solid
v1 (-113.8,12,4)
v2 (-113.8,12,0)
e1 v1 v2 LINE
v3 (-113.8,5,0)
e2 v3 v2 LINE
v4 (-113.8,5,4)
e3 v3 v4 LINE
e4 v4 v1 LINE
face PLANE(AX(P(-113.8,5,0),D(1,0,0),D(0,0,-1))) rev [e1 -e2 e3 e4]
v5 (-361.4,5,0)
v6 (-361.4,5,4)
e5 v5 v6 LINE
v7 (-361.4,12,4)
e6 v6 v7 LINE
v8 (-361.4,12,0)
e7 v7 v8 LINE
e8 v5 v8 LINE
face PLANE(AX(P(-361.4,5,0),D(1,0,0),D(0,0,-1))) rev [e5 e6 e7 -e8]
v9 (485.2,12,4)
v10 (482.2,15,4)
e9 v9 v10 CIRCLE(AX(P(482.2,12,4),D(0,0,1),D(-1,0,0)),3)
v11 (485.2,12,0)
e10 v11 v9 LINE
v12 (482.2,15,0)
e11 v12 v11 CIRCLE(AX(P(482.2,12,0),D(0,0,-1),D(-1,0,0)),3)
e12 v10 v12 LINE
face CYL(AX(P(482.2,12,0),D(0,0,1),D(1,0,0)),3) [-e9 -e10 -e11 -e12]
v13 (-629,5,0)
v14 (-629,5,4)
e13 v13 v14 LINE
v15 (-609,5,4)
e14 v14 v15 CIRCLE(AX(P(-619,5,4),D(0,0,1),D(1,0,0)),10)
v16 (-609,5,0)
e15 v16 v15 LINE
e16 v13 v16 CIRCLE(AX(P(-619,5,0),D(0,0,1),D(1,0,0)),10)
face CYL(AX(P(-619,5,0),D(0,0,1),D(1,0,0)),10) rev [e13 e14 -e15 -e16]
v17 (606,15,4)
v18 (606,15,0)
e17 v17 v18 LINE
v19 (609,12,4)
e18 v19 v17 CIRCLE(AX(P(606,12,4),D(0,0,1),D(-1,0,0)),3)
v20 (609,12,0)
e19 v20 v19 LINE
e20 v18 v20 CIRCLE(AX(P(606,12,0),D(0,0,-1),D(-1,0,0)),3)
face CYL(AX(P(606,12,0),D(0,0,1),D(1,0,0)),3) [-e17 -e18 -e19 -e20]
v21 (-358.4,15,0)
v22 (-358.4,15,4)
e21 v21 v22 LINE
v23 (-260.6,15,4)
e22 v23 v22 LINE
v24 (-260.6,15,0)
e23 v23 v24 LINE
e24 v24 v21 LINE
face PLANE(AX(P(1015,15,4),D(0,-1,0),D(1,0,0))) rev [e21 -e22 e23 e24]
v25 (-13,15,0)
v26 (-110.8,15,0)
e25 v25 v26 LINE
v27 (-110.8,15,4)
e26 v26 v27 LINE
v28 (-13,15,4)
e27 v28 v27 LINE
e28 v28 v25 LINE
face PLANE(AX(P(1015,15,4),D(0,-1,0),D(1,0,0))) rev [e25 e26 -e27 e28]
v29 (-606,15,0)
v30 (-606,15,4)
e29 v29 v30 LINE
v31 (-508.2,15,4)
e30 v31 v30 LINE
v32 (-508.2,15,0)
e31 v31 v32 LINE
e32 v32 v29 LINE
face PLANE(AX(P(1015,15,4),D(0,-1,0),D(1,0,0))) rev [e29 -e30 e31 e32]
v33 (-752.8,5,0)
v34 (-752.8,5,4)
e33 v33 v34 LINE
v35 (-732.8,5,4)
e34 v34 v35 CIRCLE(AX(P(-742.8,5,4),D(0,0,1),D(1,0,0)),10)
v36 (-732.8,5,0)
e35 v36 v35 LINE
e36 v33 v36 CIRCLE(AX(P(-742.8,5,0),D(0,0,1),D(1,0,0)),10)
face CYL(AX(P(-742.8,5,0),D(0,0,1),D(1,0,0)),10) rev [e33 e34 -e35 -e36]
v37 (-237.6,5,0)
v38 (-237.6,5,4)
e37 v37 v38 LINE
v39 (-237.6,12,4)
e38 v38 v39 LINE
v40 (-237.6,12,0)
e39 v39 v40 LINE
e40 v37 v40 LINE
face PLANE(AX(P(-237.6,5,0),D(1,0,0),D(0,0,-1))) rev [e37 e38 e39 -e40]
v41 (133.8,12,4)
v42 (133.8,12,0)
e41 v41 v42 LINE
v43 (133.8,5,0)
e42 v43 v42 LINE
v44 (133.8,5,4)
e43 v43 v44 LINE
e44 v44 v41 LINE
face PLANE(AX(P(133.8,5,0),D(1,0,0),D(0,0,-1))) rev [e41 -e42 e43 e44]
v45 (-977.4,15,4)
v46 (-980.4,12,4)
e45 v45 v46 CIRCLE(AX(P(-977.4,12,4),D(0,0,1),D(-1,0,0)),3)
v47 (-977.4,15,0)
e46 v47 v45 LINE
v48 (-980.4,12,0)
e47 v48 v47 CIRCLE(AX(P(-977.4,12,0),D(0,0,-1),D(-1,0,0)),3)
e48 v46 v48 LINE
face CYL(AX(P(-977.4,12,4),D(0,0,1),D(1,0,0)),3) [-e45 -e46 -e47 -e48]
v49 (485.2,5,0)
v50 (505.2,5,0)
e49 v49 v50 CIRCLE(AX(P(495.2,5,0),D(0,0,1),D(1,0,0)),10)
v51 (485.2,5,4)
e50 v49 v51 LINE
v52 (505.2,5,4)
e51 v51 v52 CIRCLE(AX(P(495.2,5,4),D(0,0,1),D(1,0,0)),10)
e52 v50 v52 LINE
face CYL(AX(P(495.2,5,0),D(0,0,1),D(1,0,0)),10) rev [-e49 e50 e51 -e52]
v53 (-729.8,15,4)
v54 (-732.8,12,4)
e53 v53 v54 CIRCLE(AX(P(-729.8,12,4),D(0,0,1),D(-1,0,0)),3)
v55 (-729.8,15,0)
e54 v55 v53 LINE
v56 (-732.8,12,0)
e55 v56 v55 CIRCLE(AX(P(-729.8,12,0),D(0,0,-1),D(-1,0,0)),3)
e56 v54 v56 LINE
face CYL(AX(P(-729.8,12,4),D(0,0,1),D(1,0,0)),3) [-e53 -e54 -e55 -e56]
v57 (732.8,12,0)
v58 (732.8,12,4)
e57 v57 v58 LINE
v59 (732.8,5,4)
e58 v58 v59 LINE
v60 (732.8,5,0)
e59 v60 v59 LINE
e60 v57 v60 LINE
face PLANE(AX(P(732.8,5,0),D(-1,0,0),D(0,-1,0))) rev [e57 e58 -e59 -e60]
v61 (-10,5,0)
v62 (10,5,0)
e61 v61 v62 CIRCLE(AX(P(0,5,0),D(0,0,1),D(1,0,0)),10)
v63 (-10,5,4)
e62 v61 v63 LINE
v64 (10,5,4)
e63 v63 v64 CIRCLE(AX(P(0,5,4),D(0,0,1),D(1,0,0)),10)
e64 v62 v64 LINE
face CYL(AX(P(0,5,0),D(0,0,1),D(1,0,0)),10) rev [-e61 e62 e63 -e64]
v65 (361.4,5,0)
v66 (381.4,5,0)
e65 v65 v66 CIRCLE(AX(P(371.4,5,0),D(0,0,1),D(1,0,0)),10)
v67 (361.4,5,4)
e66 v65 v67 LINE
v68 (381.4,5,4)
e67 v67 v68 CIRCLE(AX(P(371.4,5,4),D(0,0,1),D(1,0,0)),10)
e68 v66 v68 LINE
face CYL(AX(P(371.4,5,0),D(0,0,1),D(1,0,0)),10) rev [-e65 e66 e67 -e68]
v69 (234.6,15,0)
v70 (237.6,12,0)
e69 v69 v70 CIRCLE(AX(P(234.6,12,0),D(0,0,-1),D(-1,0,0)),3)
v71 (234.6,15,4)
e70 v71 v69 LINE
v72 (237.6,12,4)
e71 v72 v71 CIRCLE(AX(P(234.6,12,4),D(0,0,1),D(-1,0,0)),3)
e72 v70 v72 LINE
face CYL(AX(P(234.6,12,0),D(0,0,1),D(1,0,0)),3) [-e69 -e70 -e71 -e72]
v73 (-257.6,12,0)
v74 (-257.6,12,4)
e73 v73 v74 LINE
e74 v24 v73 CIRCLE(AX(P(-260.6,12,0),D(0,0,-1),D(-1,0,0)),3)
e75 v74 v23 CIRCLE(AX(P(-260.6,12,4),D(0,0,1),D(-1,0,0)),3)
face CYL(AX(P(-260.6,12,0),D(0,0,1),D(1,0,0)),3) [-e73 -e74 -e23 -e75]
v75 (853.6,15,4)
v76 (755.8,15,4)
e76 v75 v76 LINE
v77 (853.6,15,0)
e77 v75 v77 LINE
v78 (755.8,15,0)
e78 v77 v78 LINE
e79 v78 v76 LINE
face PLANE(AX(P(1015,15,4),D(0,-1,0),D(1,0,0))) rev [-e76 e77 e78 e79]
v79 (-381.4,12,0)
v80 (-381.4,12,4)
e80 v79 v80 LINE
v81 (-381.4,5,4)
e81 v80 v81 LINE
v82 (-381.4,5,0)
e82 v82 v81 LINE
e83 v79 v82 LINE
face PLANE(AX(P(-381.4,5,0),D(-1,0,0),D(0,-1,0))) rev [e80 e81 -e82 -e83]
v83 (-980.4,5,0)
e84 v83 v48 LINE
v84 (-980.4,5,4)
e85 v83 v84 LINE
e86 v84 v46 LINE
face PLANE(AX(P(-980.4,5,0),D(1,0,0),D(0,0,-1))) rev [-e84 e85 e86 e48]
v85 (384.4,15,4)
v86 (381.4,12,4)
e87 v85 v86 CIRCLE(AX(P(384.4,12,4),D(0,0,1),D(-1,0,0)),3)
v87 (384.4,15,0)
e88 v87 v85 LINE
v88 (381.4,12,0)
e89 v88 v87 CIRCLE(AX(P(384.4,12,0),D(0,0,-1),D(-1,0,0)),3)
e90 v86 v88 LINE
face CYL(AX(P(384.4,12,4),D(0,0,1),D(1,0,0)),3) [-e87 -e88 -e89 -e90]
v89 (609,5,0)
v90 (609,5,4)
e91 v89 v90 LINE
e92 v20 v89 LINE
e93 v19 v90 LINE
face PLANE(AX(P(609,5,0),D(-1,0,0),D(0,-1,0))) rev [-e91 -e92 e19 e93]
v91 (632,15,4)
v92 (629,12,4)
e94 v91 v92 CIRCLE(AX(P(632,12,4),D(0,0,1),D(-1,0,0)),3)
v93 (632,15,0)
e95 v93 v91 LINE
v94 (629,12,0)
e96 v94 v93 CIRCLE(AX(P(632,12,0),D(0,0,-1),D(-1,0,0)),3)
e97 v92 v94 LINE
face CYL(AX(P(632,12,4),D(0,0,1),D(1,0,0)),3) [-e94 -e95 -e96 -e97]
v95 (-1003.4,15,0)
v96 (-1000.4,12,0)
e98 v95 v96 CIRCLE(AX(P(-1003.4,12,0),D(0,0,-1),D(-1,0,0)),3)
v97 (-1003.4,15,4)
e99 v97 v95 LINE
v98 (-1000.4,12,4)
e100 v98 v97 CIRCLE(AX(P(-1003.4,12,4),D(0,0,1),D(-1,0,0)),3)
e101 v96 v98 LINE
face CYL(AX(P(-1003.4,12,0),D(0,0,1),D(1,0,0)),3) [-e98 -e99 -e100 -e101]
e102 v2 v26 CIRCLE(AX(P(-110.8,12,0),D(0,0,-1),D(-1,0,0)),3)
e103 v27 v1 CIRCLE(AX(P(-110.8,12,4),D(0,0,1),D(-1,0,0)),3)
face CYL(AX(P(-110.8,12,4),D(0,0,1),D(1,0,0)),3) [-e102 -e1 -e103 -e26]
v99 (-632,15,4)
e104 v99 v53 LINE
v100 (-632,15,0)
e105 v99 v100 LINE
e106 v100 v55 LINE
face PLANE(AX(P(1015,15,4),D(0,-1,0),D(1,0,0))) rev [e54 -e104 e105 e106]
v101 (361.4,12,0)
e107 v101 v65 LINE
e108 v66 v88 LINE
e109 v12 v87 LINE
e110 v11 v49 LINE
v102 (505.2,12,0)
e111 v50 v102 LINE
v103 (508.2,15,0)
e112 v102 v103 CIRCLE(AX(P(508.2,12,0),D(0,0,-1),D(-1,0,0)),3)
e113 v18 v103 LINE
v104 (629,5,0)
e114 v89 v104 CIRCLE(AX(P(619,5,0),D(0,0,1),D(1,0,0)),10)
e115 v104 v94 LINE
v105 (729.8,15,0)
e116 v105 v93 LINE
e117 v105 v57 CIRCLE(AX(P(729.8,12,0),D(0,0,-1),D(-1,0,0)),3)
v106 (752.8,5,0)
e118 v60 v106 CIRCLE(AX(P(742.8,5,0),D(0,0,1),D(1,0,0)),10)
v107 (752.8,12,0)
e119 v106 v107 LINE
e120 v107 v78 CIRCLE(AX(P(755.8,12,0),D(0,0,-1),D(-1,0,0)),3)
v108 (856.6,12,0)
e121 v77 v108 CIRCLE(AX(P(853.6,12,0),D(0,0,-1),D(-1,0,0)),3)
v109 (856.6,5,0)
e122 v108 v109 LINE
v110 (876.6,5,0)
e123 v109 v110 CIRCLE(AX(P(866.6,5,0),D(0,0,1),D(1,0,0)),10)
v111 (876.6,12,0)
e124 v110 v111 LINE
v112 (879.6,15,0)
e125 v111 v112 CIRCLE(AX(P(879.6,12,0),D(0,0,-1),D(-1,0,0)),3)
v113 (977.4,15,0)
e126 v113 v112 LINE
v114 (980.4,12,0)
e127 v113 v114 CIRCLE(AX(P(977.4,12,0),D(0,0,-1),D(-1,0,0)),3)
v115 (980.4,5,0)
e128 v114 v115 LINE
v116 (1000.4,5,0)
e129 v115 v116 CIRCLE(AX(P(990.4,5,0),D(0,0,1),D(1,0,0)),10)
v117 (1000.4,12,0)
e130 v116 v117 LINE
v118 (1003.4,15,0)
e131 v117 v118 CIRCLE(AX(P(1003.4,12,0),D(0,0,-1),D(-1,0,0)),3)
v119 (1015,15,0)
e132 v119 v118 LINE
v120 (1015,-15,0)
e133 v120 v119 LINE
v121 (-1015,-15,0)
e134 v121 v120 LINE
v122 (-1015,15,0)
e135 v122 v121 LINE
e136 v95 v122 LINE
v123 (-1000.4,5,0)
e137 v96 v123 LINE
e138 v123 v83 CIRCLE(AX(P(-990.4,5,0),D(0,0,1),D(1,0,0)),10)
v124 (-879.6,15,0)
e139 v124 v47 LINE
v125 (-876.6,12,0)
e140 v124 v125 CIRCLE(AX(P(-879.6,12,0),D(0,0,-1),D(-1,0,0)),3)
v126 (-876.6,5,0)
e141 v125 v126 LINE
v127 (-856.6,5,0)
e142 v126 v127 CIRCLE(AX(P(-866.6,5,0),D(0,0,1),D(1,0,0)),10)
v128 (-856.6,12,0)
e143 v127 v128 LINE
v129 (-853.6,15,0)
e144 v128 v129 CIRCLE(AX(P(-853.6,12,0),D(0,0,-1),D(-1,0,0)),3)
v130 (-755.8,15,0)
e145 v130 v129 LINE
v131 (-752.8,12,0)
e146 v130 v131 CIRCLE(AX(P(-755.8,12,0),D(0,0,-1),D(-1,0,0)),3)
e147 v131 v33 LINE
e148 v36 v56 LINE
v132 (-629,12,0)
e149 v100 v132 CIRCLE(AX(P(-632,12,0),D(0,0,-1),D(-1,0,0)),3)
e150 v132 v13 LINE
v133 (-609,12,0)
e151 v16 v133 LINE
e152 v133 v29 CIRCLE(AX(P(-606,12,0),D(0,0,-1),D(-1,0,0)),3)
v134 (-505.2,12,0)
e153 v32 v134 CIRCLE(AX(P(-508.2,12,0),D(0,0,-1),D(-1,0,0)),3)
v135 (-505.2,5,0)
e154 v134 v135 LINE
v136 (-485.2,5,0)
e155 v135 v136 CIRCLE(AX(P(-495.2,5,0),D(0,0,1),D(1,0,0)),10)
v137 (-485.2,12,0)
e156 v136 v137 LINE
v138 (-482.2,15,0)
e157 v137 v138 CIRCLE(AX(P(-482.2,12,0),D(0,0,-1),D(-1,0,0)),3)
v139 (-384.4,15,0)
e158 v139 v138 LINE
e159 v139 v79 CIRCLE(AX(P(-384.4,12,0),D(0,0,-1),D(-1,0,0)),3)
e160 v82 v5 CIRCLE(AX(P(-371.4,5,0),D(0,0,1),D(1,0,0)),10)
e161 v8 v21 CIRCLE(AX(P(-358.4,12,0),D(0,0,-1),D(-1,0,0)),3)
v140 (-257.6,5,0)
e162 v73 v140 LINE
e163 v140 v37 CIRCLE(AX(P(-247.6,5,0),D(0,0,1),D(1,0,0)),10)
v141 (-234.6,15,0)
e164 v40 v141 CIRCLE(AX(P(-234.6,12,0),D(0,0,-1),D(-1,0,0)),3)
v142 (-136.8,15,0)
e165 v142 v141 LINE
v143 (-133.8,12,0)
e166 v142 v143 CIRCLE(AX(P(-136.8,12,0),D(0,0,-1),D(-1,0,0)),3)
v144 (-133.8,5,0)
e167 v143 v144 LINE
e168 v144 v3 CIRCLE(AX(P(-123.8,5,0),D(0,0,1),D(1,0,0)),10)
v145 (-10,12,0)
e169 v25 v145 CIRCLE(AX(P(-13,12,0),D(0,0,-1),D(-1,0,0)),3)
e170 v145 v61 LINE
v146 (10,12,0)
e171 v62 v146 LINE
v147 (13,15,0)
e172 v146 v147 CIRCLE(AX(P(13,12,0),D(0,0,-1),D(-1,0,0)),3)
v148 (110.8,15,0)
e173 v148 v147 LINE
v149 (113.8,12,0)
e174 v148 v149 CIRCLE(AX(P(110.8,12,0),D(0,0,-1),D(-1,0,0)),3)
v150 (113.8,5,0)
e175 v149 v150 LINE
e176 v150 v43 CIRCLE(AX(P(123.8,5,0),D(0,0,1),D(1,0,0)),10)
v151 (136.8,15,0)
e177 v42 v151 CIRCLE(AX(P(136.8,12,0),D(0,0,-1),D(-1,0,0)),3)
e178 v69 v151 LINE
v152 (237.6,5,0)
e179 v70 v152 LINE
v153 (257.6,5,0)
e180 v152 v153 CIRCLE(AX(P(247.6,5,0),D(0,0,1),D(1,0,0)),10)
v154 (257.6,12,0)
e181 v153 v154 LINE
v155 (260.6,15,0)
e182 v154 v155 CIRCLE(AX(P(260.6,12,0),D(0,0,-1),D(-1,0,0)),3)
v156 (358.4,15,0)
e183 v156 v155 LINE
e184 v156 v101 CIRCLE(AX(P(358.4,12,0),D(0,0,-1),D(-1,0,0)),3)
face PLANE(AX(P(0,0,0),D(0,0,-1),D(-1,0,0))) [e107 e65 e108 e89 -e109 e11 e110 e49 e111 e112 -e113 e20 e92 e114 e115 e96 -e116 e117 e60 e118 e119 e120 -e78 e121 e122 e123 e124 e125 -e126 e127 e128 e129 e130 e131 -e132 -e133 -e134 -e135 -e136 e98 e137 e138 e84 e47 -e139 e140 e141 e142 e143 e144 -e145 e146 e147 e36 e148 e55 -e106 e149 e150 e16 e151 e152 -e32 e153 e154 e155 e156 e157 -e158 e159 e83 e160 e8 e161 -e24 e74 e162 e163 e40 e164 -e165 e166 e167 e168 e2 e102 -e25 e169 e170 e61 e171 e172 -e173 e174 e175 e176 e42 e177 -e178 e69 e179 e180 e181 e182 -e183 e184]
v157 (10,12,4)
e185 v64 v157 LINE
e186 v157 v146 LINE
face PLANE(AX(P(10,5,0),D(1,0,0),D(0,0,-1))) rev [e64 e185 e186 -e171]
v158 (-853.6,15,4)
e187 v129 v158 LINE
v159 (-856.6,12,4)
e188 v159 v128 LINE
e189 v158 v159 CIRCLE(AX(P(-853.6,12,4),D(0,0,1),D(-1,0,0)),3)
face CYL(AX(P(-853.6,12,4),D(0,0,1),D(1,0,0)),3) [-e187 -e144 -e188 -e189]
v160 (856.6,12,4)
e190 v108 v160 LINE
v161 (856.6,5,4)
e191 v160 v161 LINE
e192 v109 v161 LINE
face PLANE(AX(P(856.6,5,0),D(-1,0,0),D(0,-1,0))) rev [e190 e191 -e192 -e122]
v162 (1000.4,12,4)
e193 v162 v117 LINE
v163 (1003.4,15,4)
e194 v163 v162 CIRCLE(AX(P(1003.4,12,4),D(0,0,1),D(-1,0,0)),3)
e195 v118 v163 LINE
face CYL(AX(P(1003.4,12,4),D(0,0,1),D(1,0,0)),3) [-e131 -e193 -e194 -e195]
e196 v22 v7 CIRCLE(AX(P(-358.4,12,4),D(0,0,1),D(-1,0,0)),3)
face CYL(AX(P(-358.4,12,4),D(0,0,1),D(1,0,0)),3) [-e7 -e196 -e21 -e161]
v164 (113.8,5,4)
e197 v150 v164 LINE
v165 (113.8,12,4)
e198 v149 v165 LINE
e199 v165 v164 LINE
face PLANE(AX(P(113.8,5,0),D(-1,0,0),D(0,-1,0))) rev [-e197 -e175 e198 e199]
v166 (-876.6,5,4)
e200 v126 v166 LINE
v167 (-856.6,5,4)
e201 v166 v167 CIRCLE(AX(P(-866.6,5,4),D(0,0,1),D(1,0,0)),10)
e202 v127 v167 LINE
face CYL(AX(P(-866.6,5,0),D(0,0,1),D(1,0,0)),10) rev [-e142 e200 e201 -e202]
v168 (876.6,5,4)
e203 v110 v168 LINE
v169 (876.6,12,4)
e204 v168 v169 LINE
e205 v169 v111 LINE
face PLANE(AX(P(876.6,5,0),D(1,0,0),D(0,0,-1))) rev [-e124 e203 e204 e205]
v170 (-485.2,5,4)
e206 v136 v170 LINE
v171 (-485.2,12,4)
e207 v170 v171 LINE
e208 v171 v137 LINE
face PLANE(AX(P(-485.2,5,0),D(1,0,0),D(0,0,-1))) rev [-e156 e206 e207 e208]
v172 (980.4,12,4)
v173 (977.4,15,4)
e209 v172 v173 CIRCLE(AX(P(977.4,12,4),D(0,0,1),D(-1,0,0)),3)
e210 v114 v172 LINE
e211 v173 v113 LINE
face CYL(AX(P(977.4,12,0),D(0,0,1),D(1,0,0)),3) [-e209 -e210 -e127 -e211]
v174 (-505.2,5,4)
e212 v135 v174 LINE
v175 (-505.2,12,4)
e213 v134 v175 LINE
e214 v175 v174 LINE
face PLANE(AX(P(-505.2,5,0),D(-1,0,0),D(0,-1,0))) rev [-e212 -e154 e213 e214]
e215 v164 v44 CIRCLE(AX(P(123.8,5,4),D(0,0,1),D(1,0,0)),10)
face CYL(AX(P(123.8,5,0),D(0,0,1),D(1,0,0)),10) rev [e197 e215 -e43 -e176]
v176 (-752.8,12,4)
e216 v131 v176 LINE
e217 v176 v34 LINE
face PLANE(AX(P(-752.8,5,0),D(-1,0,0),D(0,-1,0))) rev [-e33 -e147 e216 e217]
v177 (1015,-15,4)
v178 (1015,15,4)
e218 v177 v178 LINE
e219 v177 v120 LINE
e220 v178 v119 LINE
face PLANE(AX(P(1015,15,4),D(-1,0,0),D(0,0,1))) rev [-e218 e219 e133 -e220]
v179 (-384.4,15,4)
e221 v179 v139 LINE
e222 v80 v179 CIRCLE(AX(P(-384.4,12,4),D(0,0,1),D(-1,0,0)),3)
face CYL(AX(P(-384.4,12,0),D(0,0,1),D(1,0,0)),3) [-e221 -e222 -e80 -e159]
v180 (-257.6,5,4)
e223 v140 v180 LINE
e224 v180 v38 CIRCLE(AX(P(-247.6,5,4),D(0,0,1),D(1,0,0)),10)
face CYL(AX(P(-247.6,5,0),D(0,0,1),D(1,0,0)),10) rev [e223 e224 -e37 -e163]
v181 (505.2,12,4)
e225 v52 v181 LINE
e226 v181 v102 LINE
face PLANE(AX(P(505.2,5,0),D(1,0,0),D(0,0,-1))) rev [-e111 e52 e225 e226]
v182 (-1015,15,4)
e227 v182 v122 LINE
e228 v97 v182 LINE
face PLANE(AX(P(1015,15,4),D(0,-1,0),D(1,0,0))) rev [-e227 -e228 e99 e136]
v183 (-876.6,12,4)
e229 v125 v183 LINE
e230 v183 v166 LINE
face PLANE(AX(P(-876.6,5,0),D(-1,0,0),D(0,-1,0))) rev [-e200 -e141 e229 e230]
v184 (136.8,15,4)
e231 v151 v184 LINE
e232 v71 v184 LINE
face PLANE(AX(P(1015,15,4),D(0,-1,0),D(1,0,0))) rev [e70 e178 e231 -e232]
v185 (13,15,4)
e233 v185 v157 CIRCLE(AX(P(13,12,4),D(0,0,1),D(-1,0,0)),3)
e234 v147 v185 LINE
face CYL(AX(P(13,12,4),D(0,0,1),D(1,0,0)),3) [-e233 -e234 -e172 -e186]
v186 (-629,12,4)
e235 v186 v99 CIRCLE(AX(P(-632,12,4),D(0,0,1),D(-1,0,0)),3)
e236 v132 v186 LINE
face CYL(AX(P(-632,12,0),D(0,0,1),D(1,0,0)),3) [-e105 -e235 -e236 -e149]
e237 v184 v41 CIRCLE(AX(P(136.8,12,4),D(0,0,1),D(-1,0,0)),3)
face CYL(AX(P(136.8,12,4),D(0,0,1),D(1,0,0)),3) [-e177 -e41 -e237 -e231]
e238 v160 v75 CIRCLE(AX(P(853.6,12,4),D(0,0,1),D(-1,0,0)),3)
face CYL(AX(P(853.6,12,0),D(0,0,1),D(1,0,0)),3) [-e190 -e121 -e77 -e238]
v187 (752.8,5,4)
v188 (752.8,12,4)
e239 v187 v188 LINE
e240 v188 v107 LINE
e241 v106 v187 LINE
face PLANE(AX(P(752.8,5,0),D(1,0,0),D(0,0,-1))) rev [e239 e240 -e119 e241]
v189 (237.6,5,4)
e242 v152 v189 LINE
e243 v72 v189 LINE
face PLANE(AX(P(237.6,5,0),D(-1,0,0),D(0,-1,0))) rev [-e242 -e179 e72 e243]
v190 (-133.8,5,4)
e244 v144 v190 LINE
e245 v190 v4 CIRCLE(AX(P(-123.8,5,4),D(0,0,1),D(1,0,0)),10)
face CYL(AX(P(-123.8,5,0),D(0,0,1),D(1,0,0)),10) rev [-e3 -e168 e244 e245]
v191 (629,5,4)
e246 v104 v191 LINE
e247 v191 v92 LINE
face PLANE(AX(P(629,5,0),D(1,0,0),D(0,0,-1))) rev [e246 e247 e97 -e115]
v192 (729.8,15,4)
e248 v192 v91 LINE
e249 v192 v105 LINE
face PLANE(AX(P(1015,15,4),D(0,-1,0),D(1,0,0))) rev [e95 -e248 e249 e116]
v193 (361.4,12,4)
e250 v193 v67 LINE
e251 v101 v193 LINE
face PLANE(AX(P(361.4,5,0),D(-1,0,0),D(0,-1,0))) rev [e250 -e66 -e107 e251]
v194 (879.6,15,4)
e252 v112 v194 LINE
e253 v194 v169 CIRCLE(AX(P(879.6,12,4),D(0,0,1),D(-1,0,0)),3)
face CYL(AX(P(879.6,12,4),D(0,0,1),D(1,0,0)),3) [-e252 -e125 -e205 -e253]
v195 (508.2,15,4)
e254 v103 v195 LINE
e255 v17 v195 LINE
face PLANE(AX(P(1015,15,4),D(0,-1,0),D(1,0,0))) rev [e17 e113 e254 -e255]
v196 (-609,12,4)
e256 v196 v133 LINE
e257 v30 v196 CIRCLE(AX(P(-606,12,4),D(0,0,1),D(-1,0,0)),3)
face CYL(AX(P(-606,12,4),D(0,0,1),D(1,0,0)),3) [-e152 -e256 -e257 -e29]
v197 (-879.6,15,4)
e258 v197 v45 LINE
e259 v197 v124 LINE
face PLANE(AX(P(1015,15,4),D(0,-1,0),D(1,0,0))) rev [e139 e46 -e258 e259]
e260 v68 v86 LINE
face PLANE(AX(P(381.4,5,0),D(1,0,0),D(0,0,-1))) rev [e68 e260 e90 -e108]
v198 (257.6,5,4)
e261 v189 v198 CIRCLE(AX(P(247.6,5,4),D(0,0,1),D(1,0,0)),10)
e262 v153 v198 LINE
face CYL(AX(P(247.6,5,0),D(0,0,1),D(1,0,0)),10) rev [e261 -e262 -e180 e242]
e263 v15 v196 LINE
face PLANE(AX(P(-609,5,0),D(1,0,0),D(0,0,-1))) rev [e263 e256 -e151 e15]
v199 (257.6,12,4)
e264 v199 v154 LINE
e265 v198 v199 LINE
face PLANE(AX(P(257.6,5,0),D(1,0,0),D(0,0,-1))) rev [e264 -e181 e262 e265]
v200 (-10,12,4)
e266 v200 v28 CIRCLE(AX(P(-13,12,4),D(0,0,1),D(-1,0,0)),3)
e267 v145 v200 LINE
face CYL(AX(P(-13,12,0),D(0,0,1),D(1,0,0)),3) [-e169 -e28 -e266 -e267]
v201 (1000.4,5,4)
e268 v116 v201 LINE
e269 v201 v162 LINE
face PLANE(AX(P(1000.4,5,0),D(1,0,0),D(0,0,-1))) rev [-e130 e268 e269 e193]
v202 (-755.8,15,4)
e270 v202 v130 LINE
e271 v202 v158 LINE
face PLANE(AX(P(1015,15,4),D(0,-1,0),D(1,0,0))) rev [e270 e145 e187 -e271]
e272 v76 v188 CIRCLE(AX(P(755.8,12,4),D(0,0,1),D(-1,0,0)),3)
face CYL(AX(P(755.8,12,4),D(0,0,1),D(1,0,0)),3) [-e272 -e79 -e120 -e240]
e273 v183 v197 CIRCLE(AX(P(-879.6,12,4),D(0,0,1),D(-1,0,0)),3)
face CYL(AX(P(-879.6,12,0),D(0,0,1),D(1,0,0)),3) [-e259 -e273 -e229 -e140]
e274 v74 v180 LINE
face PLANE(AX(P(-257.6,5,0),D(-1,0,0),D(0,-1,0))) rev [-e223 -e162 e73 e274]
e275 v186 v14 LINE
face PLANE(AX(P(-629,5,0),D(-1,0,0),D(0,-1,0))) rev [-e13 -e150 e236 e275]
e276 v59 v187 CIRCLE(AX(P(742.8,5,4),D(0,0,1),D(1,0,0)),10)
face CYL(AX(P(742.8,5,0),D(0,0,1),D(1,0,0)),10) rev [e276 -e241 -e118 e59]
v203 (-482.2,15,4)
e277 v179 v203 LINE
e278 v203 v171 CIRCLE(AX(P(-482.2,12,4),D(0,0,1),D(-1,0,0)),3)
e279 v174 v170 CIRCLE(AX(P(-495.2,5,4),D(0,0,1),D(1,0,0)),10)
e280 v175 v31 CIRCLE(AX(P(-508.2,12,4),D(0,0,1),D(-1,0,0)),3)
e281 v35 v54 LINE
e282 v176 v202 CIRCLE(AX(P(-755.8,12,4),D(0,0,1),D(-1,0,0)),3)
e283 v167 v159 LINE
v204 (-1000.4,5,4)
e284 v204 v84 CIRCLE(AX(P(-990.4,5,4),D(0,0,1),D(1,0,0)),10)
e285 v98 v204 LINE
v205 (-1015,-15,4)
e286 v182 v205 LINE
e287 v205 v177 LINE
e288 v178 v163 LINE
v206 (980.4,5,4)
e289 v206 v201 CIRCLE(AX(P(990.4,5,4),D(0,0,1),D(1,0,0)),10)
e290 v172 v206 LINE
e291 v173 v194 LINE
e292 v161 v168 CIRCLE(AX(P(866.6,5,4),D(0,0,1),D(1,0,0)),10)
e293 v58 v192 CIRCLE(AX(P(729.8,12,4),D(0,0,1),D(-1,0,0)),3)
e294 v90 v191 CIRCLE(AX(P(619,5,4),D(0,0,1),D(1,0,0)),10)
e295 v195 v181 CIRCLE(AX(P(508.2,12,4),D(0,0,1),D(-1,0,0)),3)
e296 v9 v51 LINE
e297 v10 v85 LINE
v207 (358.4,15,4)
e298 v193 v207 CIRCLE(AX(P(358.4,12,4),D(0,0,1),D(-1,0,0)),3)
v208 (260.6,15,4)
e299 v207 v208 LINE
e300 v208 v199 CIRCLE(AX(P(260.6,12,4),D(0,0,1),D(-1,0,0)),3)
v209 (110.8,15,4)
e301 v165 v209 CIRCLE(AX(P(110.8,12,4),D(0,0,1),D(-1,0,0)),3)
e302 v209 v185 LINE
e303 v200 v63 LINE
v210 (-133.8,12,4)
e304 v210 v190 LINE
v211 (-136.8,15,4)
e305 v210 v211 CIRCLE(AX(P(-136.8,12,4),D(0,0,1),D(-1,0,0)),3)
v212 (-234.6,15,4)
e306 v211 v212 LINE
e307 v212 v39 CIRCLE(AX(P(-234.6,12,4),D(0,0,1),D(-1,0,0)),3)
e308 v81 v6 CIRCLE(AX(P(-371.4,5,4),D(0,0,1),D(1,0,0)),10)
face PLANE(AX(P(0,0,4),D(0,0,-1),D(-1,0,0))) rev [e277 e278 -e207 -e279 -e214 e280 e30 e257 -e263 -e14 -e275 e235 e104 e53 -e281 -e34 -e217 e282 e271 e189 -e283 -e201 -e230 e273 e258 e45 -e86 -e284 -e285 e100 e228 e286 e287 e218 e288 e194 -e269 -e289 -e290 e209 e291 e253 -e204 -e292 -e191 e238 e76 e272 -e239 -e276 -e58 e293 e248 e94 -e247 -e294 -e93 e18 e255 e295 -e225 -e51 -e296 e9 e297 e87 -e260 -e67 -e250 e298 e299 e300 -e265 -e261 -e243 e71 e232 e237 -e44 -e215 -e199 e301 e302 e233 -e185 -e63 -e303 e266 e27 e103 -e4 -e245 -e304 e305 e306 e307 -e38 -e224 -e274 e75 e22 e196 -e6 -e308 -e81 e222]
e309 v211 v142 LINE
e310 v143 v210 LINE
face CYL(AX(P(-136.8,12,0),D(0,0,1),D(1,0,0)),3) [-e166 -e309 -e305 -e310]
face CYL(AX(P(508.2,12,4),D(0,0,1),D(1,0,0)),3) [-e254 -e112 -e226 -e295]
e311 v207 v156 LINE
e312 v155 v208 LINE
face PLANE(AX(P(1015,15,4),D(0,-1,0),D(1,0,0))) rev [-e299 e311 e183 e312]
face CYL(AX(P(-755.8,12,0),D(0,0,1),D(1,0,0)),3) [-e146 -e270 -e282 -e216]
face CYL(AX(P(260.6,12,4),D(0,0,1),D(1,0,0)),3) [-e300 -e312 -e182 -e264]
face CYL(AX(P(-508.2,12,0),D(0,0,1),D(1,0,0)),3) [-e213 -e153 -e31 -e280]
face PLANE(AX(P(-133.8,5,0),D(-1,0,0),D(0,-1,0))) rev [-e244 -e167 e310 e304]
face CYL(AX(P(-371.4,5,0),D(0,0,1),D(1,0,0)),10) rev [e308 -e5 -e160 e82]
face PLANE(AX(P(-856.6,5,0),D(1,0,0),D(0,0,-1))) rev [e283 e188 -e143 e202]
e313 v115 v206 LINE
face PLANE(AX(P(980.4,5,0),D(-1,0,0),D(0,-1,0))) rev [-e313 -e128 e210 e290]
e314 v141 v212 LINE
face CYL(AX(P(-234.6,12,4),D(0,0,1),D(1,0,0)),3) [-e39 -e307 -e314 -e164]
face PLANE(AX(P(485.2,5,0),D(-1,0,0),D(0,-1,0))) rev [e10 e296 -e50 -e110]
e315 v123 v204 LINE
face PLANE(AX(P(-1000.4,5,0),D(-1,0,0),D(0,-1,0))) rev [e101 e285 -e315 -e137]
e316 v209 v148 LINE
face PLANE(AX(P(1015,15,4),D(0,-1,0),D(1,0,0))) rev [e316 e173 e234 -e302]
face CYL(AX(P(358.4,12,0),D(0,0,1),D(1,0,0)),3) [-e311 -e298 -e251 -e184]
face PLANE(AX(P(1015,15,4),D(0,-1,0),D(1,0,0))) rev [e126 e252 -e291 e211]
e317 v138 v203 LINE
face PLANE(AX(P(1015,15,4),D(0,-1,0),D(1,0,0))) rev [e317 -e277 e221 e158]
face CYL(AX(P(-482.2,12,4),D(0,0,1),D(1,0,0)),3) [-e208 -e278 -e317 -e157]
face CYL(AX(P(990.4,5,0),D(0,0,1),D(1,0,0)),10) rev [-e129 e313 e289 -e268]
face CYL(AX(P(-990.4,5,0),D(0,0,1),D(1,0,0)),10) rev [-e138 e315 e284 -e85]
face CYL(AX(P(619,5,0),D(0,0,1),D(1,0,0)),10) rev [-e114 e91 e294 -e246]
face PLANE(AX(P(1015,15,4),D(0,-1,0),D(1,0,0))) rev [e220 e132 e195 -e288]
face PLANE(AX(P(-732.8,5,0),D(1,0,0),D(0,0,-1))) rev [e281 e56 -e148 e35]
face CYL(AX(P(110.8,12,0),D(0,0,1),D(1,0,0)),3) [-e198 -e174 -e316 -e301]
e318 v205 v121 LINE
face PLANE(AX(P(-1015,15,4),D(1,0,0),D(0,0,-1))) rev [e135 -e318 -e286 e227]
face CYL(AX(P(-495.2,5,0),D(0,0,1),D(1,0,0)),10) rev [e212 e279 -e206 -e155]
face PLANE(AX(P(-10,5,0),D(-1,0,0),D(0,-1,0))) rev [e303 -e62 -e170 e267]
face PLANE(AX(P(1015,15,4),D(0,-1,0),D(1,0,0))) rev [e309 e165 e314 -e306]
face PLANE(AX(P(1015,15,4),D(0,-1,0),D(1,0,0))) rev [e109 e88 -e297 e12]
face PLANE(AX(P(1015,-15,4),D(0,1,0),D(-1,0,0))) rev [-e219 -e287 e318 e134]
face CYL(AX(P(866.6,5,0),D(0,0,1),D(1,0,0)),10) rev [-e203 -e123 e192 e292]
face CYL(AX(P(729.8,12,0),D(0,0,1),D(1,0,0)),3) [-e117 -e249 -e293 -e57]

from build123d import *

# Parameters (mm, degrees)
SKETCH_1_W          = 2030
SKETCH_1_H          = 30
EXTRUDE_1_DEPTH     = 4
CUT_EXTRUDE_1_DEPTH = 4
FILLET_1_R          = 3


with BuildPart() as part:
    # 草图1 → 凸台-拉伸1 (new body)
    with BuildSketch(Plane.XY):
        Rectangle(SKETCH_1_W, SKETCH_1_H)
    extrude(amount=EXTRUDE_1_DEPTH)

    # 草图2 → 切除-拉伸1 (cut)
    with BuildSketch(Plane.XY.offset(4)):
        with BuildLine():
            Line((-1000.4, 5), (-1000.4, 15))
            Line((-1000.4, 15), (-980.4, 15))
            Line((-980.4, 15), (-980.4, 5))
            ThreePointArc((-980.4, 5), (-990.4, -5), (-1000.4, 5))
        make_face()
        with BuildLine():
            Line((-856.6, 15), (-876.6, 15))
            Line((-876.6, 15), (-876.6, 5))
            ThreePointArc((-876.6, 5), (-866.6, -5), (-856.6, 5))
            Line((-856.6, 5), (-856.6, 15))
        make_face()
        with BuildLine():
            Line((-732.8, 15), (-752.8, 15))
            Line((-752.8, 15), (-752.8, 5))
            ThreePointArc((-752.8, 5), (-742.8, -5), (-732.8, 5))
            Line((-732.8, 5), (-732.8, 15))
        make_face()
        with BuildLine():
            Line((-609, 15), (-629, 15))
            Line((-629, 15), (-629, 5))
            ThreePointArc((-629, 5), (-619, -5), (-609, 5))
            Line((-609, 5), (-609, 15))
        make_face()
        with BuildLine():
            Line((-485.2, 15), (-505.2, 15))
            Line((-505.2, 15), (-505.2, 5))
            ThreePointArc((-505.2, 5), (-495.2, -5), (-485.2, 5))
            Line((-485.2, 5), (-485.2, 15))
        make_face()
        with BuildLine():
            Line((-361.4, 15), (-381.4, 15))
            Line((-381.4, 15), (-381.4, 5))
            ThreePointArc((-381.4, 5), (-371.4, -5), (-361.4, 5))
            Line((-361.4, 5), (-361.4, 15))
        make_face()
        with BuildLine():
            Line((-237.6, 15), (-257.6, 15))
            Line((-257.6, 15), (-257.6, 5))
            ThreePointArc((-257.6, 5), (-247.6, -5), (-237.6, 5))
            Line((-237.6, 5), (-237.6, 15))
        make_face()
        with BuildLine():
            Line((-113.8, 15), (-133.8, 15))
            Line((-133.8, 15), (-133.8, 5))
            ThreePointArc((-133.8, 5), (-123.8, -5), (-113.8, 5))
            Line((-113.8, 5), (-113.8, 15))
        make_face()
        with BuildLine():
            Line((10, 15), (-10, 15))
            Line((-10, 15), (-10, 5))
            ThreePointArc((-10, 5), (0, -5), (10, 5))
            Line((10, 5), (10, 15))
        make_face()
        with BuildLine():
            Line((133.8, 15), (113.8, 15))
            Line((113.8, 15), (113.8, 5))
            ThreePointArc((113.8, 5), (123.8, -5), (133.8, 5))
            Line((133.8, 5), (133.8, 15))
        make_face()
        with BuildLine():
            Line((257.6, 15), (237.6, 15))
            Line((237.6, 15), (237.6, 5))
            ThreePointArc((237.6, 5), (247.6, -5), (257.6, 5))
            Line((257.6, 5), (257.6, 15))
        make_face()
        with BuildLine():
            Line((381.4, 15), (361.4, 15))
            Line((361.4, 15), (361.4, 5))
            ThreePointArc((361.4, 5), (371.4, -5), (381.4, 5))
            Line((381.4, 5), (381.4, 15))
        make_face()
        with BuildLine():
            Line((505.2, 15), (485.2, 15))
            Line((485.2, 15), (485.2, 5))
            ThreePointArc((485.2, 5), (495.2, -5), (505.2, 5))
            Line((505.2, 5), (505.2, 15))
        make_face()
        with BuildLine():
            Line((629, 15), (609, 15))
            Line((609, 15), (609, 5))
            ThreePointArc((609, 5), (619, -5), (629, 5))
            Line((629, 5), (629, 15))
        make_face()
        with BuildLine():
            Line((752.8, 15), (732.8, 15))
            Line((732.8, 15), (732.8, 5))
            ThreePointArc((732.8, 5), (742.8, -5), (752.8, 5))
            Line((752.8, 5), (752.8, 15))
        make_face()
        with BuildLine():
            Line((876.6, 15), (856.6, 15))
            Line((856.6, 15), (856.6, 5))
            ThreePointArc((856.6, 5), (866.6, -5), (876.6, 5))
            Line((876.6, 5), (876.6, 15))
        make_face()
        with BuildLine():
            Line((1000.4, 15), (980.4, 15))
            Line((980.4, 15), (980.4, 5))
            ThreePointArc((980.4, 5), (990.4, -5), (1000.4, 5))
            Line((1000.4, 5), (1000.4, 15))
        make_face()
    extrude(amount=-CUT_EXTRUDE_1_DEPTH, mode=Mode.SUBTRACT)

    # 圆角1
    fillet_1_edges = [part.edges().sort_by_distance(p)[0] for p in [
        (-876.6, 15, 2),
        (-856.6, 15, 2),
        (-752.8, 15, 2),
        (-732.8, 15, 2),
        (-629, 15, 2),
        (-609, 15, 2),
        (-505.2, 15, 2),
        (-485.2, 15, 2),
        (-381.4, 15, 2),
        (-361.4, 15, 2),
        (-257.6, 15, 2),
        (-237.6, 15, 2),
        (-133.8, 15, 2),
        (-113.8, 15, 2),
        (-10, 15, 2),
        (10, 15, 2),
        (113.8, 15, 2),
        (133.8, 15, 2),
        (237.6, 15, 2),
        (257.6, 15, 2),
        (361.4, 15, 2),
        (381.4, 15, 2),
        (485.2, 15, 2),
        (505.2, 15, 2),
        (609, 15, 2),
        (629, 15, 2),
        (732.8, 15, 2),
        (752.8, 15, 2),
        (856.6, 15, 2),
        (876.6, 15, 2),
        (980.4, 15, 2),
        (1000.4, 15, 2),
        (-1000.4, 15, 2),
        (-980.4, 15, 2),
    ]]
    fillet(fillet_1_edges, radius=FILLET_1_R)


solid = part.part
